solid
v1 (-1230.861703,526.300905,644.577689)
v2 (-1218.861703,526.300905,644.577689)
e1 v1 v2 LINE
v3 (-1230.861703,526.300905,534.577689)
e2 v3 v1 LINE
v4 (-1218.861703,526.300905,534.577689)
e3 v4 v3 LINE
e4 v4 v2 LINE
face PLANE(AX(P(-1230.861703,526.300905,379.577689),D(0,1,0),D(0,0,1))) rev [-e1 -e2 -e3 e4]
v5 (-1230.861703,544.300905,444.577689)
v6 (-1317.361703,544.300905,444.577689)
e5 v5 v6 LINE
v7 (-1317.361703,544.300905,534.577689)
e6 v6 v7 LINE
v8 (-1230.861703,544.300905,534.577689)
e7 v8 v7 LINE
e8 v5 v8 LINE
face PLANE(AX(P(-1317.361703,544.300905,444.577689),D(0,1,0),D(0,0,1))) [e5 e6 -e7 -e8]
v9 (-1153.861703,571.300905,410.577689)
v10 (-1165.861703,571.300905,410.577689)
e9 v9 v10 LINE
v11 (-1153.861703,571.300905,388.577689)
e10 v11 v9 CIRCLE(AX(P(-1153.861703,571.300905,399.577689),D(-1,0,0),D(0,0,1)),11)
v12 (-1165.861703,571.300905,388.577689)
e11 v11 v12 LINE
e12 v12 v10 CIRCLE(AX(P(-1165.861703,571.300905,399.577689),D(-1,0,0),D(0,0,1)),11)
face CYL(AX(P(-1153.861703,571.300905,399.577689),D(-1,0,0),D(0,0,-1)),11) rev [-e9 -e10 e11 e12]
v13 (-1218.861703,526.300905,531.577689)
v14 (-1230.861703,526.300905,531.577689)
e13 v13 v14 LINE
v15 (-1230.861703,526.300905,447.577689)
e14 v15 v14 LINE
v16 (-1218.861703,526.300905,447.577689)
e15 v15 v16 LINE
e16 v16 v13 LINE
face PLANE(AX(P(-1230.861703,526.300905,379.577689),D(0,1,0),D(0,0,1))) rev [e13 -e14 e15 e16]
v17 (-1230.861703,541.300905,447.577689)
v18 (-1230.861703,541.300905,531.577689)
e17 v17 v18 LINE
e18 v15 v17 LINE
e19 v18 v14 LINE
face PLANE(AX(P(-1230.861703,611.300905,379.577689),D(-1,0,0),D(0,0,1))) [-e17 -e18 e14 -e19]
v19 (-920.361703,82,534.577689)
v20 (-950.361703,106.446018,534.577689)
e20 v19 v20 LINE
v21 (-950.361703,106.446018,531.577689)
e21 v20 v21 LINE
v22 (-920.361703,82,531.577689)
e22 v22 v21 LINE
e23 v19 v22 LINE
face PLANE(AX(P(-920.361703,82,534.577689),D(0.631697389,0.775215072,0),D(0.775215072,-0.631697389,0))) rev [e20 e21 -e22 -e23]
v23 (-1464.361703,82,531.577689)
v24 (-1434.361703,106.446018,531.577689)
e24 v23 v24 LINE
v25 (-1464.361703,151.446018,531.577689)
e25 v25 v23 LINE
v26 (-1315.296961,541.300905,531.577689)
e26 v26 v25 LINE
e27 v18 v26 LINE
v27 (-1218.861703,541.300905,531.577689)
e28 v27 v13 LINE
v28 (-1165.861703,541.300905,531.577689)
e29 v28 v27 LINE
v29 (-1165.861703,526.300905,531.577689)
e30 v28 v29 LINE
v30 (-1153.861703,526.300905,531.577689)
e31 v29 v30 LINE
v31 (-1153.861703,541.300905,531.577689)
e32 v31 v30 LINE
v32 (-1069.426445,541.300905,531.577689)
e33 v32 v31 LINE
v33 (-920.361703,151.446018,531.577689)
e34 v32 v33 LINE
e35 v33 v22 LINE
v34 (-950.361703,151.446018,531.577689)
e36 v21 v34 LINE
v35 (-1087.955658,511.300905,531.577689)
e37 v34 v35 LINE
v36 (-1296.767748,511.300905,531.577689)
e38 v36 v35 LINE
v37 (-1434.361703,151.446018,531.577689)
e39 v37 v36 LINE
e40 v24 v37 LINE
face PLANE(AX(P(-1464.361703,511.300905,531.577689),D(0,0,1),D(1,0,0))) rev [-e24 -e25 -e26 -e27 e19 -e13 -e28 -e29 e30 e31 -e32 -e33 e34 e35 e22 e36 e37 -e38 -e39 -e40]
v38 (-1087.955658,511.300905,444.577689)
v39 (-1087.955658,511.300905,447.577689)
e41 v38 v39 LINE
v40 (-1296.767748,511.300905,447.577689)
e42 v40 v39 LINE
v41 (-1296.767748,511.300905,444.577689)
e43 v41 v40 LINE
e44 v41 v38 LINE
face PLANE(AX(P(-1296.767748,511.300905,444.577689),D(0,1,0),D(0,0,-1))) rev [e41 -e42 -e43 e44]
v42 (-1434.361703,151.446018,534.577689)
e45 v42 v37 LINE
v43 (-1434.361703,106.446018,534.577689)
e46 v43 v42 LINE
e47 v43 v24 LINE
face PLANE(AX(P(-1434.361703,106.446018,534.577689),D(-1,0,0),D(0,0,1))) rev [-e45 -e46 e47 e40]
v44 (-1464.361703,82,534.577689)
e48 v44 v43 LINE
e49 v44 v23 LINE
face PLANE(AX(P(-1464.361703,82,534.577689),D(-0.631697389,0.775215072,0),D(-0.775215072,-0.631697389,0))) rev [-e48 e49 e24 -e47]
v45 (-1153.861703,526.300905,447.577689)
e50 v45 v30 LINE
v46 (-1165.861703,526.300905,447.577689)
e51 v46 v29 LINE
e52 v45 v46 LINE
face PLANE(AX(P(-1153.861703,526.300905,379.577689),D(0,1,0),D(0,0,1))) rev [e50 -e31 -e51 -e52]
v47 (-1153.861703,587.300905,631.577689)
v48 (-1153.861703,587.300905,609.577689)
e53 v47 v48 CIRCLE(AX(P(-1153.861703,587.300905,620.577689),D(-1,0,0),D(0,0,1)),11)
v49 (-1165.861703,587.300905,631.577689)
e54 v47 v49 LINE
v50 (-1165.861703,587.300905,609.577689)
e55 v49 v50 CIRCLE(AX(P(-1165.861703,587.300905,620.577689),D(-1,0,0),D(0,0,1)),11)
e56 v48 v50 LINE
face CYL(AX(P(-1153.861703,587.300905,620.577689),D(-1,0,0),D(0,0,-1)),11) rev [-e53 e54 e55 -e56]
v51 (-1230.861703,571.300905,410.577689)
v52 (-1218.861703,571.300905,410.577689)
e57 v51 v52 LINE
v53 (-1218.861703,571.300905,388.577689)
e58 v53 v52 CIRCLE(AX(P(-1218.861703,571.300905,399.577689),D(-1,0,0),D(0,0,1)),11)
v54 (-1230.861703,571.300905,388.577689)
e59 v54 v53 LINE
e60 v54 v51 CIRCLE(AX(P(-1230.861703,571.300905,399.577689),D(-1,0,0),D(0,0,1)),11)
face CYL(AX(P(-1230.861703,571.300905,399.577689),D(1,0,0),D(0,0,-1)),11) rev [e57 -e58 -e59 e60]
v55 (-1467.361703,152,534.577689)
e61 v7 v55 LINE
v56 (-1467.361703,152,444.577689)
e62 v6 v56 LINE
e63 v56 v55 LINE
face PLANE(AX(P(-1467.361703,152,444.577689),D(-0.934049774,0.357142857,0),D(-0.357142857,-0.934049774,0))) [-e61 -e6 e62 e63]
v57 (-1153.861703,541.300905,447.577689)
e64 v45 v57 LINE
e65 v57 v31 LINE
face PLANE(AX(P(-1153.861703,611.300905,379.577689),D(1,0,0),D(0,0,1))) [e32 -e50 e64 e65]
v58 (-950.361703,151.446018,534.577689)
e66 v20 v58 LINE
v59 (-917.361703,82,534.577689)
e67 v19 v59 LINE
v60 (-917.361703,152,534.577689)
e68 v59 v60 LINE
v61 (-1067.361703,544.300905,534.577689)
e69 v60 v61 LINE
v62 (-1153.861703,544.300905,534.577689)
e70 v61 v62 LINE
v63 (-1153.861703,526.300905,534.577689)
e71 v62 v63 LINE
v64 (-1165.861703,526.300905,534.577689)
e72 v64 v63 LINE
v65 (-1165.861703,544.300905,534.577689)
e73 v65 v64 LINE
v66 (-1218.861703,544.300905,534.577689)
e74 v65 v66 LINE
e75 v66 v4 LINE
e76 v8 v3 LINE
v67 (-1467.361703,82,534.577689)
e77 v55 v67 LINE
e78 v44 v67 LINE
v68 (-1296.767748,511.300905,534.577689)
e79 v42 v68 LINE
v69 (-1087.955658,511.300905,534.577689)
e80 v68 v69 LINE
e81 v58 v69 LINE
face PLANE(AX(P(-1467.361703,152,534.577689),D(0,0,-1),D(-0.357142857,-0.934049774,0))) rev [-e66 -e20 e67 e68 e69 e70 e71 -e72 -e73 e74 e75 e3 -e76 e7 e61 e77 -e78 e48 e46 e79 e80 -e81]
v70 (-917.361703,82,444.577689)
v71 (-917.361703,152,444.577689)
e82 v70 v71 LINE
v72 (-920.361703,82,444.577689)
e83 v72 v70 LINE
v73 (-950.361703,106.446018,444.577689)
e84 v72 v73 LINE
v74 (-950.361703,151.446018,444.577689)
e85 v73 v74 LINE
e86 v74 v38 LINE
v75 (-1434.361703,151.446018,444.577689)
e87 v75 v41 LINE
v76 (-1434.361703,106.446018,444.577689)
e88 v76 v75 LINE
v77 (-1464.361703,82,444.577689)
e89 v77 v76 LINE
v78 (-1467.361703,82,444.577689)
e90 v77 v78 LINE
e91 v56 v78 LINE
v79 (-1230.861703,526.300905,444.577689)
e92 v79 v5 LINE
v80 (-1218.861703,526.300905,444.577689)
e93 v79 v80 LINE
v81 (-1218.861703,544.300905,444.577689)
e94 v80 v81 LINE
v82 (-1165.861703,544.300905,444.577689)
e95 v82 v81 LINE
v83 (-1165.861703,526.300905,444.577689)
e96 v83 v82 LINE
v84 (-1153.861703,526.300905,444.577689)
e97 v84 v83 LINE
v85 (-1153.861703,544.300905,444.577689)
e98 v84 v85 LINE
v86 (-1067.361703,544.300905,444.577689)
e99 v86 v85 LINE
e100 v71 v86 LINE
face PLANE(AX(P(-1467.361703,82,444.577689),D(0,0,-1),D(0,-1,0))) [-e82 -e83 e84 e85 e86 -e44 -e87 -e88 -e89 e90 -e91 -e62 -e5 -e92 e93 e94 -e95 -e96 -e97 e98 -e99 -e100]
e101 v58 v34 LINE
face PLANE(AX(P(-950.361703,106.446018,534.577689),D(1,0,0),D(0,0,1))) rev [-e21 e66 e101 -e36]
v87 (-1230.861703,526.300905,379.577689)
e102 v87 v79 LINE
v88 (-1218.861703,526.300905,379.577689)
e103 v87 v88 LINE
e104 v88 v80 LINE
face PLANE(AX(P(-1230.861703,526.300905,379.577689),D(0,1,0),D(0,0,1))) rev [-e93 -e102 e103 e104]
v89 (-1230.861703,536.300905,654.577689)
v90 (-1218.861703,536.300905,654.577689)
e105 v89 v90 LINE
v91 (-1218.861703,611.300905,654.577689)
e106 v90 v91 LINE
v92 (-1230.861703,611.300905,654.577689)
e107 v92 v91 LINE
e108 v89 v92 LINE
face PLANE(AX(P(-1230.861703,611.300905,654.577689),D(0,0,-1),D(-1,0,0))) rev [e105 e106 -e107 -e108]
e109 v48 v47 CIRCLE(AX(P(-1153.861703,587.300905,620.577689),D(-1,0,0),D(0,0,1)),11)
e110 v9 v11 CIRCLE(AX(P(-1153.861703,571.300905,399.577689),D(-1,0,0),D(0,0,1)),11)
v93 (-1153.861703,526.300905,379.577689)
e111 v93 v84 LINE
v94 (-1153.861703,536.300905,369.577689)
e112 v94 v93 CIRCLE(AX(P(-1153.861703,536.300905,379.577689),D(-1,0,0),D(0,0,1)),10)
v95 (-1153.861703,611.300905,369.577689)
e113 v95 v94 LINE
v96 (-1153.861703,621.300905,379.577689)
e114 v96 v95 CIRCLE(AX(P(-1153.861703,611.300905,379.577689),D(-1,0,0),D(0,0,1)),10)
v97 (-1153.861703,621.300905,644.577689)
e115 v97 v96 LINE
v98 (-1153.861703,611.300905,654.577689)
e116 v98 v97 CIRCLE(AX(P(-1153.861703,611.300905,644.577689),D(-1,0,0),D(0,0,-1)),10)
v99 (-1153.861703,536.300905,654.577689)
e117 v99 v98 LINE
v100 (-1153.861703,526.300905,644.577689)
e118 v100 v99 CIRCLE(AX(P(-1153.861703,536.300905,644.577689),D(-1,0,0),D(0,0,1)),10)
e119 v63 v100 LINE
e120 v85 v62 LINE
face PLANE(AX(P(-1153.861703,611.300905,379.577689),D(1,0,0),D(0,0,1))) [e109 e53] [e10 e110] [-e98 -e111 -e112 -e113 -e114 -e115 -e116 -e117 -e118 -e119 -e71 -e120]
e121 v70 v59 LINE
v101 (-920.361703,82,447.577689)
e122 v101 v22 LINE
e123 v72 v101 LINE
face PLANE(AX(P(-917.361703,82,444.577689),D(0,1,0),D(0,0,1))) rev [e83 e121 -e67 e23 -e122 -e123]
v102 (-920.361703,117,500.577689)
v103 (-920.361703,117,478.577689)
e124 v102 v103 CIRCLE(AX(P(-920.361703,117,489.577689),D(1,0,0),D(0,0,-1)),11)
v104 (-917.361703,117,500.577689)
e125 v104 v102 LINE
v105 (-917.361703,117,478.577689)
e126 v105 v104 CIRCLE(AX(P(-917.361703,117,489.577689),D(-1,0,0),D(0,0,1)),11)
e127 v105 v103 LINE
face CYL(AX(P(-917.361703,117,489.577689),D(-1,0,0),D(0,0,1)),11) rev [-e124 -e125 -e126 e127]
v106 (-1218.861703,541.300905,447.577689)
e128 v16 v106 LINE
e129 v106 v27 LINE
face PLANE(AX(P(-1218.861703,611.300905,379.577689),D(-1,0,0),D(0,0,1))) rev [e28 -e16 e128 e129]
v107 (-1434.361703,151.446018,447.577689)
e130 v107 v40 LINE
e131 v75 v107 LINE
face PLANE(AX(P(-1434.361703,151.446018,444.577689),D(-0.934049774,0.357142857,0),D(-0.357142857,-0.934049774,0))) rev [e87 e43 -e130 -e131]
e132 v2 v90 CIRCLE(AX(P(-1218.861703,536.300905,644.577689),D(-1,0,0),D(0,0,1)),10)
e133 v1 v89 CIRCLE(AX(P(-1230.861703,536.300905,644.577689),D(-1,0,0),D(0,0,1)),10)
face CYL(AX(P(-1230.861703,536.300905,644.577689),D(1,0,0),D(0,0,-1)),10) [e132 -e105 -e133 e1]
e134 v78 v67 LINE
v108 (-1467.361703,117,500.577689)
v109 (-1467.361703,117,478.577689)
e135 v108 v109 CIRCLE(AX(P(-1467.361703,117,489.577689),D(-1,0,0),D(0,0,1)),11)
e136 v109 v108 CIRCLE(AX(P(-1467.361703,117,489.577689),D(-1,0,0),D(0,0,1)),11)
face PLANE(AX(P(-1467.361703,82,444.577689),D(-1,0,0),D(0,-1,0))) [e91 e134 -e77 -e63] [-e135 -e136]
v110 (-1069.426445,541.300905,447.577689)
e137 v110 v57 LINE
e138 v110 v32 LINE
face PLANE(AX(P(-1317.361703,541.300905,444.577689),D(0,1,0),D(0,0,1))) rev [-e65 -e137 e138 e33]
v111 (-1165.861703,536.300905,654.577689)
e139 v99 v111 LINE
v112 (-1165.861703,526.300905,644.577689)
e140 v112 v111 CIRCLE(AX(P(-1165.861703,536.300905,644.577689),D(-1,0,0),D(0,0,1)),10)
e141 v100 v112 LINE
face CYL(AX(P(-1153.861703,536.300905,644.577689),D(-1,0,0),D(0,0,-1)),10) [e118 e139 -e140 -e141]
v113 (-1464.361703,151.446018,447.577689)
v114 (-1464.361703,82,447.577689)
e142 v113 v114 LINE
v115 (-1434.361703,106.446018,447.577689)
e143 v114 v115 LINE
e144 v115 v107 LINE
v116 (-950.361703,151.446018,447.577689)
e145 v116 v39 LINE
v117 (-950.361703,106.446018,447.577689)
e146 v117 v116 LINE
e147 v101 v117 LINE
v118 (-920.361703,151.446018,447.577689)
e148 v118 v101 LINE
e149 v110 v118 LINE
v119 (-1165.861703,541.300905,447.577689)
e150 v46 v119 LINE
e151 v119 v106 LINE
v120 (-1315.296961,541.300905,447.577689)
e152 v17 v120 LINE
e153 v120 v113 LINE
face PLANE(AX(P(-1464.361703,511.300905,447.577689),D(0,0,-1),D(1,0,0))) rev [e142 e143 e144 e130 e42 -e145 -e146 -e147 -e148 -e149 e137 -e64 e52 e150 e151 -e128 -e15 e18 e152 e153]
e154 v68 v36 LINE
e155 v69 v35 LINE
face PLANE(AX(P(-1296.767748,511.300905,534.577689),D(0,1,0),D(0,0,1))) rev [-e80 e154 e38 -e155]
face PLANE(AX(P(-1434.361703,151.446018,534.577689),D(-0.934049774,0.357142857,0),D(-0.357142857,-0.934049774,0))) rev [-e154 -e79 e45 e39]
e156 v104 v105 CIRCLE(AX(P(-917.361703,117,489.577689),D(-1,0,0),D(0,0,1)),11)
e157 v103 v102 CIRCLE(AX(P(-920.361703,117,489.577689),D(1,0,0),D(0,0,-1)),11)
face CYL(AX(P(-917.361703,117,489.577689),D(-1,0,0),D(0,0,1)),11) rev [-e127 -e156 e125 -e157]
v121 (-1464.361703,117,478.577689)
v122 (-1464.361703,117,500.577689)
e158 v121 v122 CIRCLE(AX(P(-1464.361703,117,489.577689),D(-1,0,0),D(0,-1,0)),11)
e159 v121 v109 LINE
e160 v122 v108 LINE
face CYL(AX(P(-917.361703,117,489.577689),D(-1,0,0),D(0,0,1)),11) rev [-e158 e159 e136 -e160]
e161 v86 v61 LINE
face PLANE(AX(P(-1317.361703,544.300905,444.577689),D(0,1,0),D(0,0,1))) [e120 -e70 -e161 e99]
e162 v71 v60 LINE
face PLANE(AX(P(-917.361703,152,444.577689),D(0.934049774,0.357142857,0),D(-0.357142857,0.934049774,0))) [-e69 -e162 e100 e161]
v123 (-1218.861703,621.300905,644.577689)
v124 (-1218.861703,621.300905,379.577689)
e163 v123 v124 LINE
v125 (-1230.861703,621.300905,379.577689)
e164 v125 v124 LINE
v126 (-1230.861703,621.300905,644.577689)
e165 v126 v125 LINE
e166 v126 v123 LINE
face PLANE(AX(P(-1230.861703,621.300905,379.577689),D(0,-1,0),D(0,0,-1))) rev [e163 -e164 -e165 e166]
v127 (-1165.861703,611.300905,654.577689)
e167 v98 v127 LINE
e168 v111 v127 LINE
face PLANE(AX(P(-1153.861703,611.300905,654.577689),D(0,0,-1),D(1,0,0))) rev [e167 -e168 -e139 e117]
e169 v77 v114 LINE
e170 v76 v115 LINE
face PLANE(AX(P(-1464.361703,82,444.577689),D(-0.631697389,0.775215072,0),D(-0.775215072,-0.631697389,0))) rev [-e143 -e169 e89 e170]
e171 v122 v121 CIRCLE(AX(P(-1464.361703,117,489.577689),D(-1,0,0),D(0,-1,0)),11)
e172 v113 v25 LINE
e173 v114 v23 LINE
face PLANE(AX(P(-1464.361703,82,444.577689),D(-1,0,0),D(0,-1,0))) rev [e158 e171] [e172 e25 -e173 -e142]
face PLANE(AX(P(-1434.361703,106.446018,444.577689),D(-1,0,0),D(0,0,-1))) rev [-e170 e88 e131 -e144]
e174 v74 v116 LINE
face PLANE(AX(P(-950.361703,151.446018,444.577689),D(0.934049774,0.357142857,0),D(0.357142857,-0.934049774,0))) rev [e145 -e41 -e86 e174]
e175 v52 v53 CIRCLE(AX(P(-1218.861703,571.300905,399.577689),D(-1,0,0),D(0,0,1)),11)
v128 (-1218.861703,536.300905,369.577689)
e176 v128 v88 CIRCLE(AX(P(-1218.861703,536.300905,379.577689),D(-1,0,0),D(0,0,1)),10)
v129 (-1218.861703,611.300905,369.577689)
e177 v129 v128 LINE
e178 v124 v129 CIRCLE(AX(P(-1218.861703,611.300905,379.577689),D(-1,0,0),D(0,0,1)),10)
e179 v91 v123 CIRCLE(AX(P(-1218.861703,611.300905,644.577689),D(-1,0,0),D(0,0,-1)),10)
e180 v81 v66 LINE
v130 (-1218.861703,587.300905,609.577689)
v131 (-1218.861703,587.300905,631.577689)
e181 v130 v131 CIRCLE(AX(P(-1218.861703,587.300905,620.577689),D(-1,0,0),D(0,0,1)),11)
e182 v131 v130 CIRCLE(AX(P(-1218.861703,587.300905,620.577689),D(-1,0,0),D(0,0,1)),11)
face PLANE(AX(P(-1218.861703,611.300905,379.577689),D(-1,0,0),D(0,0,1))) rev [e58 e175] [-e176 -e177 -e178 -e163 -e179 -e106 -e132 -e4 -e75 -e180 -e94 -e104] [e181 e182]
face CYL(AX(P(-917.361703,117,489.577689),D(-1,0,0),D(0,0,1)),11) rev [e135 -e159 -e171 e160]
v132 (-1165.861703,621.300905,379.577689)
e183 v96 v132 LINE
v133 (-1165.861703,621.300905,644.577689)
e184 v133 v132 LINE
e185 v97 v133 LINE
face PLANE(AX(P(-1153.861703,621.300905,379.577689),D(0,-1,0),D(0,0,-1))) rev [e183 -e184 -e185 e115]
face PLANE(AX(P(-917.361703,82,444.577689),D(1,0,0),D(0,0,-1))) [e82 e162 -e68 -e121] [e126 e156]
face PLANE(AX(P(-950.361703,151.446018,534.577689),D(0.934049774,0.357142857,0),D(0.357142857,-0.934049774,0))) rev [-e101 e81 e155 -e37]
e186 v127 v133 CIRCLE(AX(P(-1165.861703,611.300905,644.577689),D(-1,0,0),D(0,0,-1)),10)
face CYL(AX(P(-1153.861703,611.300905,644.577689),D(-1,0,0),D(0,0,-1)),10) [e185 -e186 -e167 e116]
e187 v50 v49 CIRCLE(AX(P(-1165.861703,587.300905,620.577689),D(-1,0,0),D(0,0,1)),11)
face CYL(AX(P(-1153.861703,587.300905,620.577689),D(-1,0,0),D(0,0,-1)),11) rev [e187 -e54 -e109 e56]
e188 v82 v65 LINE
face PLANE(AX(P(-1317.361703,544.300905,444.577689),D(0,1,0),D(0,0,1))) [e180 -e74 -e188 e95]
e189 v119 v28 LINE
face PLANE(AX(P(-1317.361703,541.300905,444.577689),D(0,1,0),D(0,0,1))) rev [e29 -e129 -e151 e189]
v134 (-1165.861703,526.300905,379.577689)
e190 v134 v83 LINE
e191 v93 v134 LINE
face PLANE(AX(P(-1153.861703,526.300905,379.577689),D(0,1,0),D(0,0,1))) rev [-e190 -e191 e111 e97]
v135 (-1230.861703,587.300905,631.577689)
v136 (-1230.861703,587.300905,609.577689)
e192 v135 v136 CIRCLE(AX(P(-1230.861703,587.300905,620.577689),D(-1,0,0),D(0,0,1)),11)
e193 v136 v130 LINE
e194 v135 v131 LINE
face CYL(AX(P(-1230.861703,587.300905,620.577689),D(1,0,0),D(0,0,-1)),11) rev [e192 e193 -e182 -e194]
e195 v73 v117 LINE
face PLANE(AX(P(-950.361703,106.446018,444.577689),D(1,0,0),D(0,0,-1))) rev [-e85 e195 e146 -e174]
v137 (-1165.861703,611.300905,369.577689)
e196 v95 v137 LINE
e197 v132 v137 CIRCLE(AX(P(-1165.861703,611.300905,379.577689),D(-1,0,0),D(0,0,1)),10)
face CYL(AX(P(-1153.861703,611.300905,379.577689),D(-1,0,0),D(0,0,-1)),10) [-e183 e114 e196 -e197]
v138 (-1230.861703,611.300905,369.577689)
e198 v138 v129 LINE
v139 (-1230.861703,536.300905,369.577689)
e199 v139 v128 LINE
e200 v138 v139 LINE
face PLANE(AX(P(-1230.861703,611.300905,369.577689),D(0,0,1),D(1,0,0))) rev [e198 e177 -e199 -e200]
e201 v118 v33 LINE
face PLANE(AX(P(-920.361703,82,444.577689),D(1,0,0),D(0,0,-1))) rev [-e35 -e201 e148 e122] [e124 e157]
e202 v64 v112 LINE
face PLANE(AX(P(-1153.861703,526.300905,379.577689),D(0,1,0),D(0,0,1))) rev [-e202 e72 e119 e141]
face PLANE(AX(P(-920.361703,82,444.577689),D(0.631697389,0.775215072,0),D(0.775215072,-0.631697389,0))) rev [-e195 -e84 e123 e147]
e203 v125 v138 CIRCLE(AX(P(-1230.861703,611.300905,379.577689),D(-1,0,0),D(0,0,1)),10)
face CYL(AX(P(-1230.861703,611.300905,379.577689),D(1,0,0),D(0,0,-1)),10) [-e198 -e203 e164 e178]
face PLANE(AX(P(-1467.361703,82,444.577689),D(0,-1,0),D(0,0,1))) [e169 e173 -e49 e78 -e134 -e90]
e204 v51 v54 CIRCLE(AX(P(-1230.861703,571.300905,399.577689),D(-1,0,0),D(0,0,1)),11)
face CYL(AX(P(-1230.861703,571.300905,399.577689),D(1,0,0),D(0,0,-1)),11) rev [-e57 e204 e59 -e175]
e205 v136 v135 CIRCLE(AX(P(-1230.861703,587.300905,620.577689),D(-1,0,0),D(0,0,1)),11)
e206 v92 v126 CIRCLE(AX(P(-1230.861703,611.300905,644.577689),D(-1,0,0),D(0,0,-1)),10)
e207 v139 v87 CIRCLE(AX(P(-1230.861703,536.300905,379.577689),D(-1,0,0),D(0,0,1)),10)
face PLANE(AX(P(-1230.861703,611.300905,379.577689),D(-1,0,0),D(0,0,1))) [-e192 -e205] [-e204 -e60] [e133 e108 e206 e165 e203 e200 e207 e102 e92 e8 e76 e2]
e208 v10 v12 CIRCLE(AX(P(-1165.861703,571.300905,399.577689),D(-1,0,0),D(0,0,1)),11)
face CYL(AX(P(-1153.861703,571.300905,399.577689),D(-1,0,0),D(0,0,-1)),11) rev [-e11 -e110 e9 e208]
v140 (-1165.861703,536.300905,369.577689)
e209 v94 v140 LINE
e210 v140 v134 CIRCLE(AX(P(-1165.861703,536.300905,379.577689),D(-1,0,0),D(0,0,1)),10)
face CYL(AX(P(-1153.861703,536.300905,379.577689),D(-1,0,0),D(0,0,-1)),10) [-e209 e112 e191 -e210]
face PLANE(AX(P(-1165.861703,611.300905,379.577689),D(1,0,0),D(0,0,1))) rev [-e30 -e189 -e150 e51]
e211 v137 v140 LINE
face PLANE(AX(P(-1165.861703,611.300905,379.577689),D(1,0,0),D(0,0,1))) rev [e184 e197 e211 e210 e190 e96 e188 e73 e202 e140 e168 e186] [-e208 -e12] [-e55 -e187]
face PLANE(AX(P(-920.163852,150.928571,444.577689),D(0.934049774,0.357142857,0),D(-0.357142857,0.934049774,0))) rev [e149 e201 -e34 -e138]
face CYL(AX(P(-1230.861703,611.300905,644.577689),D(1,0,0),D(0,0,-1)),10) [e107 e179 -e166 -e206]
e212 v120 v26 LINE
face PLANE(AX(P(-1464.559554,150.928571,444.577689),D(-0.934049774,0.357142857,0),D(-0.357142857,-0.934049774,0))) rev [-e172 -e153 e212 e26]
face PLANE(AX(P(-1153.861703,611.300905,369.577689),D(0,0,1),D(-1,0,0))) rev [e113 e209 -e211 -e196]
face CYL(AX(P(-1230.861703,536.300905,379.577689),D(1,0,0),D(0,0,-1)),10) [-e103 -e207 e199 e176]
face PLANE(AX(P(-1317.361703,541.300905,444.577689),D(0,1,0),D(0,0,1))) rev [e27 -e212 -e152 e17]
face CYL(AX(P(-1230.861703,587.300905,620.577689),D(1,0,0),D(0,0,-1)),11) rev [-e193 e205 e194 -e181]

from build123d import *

# Parameters (mm, degrees)
SHEET_EXTRUDE_1_1_BACK   = 45
SHEET_EXTRUDE_1_1_DEPTH  = 90
THICKEN_1_T2             = 3
EXTRUDE_START            = 42
EXTRUDE_3_DEPTH          = 3
CUT_EXTRUDE_1_DEPTH      = 811.963488807
CUT_EXTRUDE_1_DEPTH_BACK = 811.963488807
SKETCH_4_R               = 11
EXTRUDE_START_2          = 26.5
SKETCH_5_R               = 11
EXTRUDE_4_DEPTH          = 12


with BuildPart() as body_1:
    # Sheet Extrude 1: a surface, the sketch's curves swept straight by 90 mm
    with BuildLine(Plane.XY.offset(489.577688539).offset(-SHEET_EXTRUDE_1_1_BACK), mode=Mode.PRIVATE) as sheet_extrude_1_1_path:
        Line((-1467.361703007, 82), (-1467.361703007, 152))
        Line((-1467.361703007, 152), (-1317.361703007, 544.300904919))
        Line((-1317.361703007, 544.300904919), (-1067.361703007, 544.300904919))
        Line((-1067.361703007, 544.300904919), (-917.361703007, 152))
        Line((-917.361703007, 152), (-917.361703007, 82))
    sheet_extrude_1_1 = Shell.extrude(sheet_extrude_1_1_path.wire(), (0 * SHEET_EXTRUDE_1_1_DEPTH, 0 * SHEET_EXTRUDE_1_1_DEPTH, 1 * SHEET_EXTRUDE_1_1_DEPTH))
    add(Solid.thicken(sheet_extrude_1_1, -THICKEN_1_T2))

    # 草图3 → 凸台-拉伸3 (add)
    with BuildSketch(Plane.XY.offset(489.577688539).offset(EXTRUDE_START)):
        Polygon((-1464.361703007, 82), (-1434.361703007, 106.446018098), (-1434.361703007, 151.446018098), (-1296.767748095, 511.300904919), (-1192.361703007, 511.300904919), (-1192.361703007, 541.300904919), (-1315.296961402, 541.300904919), (-1464.361703007, 151.446018098), align=None)
    extrude(amount=EXTRUDE_3_DEPTH)

    # 镜向1: body 1 across plane


with BuildPart() as body_1_1:
    add(body_1.part)
    add(body_1.part.mirror(Plane.ZY.offset(1192.361703007)))

    # 镜向2: body 1 across plane


with BuildPart() as body_1_2:
    add(body_1_1.part)
    add(body_1_1.part.mirror(Plane.XY.offset(489.577688539)))

    # 草图4 → 切除-拉伸1 (cut, two sides: drawn at the far end of the back side and taken through both)
    with BuildSketch(Plane.ZY.offset(1192.361703007).offset(-CUT_EXTRUDE_1_DEPTH_BACK)):
        with Locations((489.577688539, 117)):
            Circle(SKETCH_4_R)
    extrude(amount=CUT_EXTRUDE_1_DEPTH + CUT_EXTRUDE_1_DEPTH_BACK, mode=Mode.SUBTRACT)

    # 草图5 → 凸台-拉伸4 (add)
    with BuildSketch(Plane.ZY.offset(1192.361703007).offset(EXTRUDE_START_2)):
        with BuildLine():
            Line((379.577688539, 621.300904919), (644.577688539, 621.300904919))
            ThreePointArc((644.577688539, 621.300904919), (651.64875635, 618.371972731), (654.577688539, 611.300904919))
            Line((654.577688539, 611.300904919), (654.577688539, 536.300904919))
            ThreePointArc((654.577688539, 536.300904919), (651.64875635, 529.229837107), (644.577688539, 526.300904919))
            Line((644.577688539, 526.300904919), (379.577688539, 526.300904919))
            ThreePointArc((379.577688539, 526.300904919), (372.506620727, 529.229837107), (369.577688539, 536.300904919))
            Line((369.577688539, 536.300904919), (369.577688539, 611.300904919))
            ThreePointArc((369.577688539, 611.300904919), (372.506620727, 618.371972731), (379.577688539, 621.300904919))
        make_face()
        with Locations((620.577688539, 587.300904919)):
            Circle(SKETCH_5_R, mode=Mode.SUBTRACT)
        with Locations((399.577688539, 571.300904919)):
            Circle(SKETCH_5_R, mode=Mode.SUBTRACT)
    extrude(amount=EXTRUDE_4_DEPTH)

    # 镜向3: body 1 across plane


with BuildPart() as body_1_3:
    add(body_1_2.part)
    add(body_1_2.part.mirror(Plane.ZY.offset(1192.361703007)))


solid = body_1_3.part
